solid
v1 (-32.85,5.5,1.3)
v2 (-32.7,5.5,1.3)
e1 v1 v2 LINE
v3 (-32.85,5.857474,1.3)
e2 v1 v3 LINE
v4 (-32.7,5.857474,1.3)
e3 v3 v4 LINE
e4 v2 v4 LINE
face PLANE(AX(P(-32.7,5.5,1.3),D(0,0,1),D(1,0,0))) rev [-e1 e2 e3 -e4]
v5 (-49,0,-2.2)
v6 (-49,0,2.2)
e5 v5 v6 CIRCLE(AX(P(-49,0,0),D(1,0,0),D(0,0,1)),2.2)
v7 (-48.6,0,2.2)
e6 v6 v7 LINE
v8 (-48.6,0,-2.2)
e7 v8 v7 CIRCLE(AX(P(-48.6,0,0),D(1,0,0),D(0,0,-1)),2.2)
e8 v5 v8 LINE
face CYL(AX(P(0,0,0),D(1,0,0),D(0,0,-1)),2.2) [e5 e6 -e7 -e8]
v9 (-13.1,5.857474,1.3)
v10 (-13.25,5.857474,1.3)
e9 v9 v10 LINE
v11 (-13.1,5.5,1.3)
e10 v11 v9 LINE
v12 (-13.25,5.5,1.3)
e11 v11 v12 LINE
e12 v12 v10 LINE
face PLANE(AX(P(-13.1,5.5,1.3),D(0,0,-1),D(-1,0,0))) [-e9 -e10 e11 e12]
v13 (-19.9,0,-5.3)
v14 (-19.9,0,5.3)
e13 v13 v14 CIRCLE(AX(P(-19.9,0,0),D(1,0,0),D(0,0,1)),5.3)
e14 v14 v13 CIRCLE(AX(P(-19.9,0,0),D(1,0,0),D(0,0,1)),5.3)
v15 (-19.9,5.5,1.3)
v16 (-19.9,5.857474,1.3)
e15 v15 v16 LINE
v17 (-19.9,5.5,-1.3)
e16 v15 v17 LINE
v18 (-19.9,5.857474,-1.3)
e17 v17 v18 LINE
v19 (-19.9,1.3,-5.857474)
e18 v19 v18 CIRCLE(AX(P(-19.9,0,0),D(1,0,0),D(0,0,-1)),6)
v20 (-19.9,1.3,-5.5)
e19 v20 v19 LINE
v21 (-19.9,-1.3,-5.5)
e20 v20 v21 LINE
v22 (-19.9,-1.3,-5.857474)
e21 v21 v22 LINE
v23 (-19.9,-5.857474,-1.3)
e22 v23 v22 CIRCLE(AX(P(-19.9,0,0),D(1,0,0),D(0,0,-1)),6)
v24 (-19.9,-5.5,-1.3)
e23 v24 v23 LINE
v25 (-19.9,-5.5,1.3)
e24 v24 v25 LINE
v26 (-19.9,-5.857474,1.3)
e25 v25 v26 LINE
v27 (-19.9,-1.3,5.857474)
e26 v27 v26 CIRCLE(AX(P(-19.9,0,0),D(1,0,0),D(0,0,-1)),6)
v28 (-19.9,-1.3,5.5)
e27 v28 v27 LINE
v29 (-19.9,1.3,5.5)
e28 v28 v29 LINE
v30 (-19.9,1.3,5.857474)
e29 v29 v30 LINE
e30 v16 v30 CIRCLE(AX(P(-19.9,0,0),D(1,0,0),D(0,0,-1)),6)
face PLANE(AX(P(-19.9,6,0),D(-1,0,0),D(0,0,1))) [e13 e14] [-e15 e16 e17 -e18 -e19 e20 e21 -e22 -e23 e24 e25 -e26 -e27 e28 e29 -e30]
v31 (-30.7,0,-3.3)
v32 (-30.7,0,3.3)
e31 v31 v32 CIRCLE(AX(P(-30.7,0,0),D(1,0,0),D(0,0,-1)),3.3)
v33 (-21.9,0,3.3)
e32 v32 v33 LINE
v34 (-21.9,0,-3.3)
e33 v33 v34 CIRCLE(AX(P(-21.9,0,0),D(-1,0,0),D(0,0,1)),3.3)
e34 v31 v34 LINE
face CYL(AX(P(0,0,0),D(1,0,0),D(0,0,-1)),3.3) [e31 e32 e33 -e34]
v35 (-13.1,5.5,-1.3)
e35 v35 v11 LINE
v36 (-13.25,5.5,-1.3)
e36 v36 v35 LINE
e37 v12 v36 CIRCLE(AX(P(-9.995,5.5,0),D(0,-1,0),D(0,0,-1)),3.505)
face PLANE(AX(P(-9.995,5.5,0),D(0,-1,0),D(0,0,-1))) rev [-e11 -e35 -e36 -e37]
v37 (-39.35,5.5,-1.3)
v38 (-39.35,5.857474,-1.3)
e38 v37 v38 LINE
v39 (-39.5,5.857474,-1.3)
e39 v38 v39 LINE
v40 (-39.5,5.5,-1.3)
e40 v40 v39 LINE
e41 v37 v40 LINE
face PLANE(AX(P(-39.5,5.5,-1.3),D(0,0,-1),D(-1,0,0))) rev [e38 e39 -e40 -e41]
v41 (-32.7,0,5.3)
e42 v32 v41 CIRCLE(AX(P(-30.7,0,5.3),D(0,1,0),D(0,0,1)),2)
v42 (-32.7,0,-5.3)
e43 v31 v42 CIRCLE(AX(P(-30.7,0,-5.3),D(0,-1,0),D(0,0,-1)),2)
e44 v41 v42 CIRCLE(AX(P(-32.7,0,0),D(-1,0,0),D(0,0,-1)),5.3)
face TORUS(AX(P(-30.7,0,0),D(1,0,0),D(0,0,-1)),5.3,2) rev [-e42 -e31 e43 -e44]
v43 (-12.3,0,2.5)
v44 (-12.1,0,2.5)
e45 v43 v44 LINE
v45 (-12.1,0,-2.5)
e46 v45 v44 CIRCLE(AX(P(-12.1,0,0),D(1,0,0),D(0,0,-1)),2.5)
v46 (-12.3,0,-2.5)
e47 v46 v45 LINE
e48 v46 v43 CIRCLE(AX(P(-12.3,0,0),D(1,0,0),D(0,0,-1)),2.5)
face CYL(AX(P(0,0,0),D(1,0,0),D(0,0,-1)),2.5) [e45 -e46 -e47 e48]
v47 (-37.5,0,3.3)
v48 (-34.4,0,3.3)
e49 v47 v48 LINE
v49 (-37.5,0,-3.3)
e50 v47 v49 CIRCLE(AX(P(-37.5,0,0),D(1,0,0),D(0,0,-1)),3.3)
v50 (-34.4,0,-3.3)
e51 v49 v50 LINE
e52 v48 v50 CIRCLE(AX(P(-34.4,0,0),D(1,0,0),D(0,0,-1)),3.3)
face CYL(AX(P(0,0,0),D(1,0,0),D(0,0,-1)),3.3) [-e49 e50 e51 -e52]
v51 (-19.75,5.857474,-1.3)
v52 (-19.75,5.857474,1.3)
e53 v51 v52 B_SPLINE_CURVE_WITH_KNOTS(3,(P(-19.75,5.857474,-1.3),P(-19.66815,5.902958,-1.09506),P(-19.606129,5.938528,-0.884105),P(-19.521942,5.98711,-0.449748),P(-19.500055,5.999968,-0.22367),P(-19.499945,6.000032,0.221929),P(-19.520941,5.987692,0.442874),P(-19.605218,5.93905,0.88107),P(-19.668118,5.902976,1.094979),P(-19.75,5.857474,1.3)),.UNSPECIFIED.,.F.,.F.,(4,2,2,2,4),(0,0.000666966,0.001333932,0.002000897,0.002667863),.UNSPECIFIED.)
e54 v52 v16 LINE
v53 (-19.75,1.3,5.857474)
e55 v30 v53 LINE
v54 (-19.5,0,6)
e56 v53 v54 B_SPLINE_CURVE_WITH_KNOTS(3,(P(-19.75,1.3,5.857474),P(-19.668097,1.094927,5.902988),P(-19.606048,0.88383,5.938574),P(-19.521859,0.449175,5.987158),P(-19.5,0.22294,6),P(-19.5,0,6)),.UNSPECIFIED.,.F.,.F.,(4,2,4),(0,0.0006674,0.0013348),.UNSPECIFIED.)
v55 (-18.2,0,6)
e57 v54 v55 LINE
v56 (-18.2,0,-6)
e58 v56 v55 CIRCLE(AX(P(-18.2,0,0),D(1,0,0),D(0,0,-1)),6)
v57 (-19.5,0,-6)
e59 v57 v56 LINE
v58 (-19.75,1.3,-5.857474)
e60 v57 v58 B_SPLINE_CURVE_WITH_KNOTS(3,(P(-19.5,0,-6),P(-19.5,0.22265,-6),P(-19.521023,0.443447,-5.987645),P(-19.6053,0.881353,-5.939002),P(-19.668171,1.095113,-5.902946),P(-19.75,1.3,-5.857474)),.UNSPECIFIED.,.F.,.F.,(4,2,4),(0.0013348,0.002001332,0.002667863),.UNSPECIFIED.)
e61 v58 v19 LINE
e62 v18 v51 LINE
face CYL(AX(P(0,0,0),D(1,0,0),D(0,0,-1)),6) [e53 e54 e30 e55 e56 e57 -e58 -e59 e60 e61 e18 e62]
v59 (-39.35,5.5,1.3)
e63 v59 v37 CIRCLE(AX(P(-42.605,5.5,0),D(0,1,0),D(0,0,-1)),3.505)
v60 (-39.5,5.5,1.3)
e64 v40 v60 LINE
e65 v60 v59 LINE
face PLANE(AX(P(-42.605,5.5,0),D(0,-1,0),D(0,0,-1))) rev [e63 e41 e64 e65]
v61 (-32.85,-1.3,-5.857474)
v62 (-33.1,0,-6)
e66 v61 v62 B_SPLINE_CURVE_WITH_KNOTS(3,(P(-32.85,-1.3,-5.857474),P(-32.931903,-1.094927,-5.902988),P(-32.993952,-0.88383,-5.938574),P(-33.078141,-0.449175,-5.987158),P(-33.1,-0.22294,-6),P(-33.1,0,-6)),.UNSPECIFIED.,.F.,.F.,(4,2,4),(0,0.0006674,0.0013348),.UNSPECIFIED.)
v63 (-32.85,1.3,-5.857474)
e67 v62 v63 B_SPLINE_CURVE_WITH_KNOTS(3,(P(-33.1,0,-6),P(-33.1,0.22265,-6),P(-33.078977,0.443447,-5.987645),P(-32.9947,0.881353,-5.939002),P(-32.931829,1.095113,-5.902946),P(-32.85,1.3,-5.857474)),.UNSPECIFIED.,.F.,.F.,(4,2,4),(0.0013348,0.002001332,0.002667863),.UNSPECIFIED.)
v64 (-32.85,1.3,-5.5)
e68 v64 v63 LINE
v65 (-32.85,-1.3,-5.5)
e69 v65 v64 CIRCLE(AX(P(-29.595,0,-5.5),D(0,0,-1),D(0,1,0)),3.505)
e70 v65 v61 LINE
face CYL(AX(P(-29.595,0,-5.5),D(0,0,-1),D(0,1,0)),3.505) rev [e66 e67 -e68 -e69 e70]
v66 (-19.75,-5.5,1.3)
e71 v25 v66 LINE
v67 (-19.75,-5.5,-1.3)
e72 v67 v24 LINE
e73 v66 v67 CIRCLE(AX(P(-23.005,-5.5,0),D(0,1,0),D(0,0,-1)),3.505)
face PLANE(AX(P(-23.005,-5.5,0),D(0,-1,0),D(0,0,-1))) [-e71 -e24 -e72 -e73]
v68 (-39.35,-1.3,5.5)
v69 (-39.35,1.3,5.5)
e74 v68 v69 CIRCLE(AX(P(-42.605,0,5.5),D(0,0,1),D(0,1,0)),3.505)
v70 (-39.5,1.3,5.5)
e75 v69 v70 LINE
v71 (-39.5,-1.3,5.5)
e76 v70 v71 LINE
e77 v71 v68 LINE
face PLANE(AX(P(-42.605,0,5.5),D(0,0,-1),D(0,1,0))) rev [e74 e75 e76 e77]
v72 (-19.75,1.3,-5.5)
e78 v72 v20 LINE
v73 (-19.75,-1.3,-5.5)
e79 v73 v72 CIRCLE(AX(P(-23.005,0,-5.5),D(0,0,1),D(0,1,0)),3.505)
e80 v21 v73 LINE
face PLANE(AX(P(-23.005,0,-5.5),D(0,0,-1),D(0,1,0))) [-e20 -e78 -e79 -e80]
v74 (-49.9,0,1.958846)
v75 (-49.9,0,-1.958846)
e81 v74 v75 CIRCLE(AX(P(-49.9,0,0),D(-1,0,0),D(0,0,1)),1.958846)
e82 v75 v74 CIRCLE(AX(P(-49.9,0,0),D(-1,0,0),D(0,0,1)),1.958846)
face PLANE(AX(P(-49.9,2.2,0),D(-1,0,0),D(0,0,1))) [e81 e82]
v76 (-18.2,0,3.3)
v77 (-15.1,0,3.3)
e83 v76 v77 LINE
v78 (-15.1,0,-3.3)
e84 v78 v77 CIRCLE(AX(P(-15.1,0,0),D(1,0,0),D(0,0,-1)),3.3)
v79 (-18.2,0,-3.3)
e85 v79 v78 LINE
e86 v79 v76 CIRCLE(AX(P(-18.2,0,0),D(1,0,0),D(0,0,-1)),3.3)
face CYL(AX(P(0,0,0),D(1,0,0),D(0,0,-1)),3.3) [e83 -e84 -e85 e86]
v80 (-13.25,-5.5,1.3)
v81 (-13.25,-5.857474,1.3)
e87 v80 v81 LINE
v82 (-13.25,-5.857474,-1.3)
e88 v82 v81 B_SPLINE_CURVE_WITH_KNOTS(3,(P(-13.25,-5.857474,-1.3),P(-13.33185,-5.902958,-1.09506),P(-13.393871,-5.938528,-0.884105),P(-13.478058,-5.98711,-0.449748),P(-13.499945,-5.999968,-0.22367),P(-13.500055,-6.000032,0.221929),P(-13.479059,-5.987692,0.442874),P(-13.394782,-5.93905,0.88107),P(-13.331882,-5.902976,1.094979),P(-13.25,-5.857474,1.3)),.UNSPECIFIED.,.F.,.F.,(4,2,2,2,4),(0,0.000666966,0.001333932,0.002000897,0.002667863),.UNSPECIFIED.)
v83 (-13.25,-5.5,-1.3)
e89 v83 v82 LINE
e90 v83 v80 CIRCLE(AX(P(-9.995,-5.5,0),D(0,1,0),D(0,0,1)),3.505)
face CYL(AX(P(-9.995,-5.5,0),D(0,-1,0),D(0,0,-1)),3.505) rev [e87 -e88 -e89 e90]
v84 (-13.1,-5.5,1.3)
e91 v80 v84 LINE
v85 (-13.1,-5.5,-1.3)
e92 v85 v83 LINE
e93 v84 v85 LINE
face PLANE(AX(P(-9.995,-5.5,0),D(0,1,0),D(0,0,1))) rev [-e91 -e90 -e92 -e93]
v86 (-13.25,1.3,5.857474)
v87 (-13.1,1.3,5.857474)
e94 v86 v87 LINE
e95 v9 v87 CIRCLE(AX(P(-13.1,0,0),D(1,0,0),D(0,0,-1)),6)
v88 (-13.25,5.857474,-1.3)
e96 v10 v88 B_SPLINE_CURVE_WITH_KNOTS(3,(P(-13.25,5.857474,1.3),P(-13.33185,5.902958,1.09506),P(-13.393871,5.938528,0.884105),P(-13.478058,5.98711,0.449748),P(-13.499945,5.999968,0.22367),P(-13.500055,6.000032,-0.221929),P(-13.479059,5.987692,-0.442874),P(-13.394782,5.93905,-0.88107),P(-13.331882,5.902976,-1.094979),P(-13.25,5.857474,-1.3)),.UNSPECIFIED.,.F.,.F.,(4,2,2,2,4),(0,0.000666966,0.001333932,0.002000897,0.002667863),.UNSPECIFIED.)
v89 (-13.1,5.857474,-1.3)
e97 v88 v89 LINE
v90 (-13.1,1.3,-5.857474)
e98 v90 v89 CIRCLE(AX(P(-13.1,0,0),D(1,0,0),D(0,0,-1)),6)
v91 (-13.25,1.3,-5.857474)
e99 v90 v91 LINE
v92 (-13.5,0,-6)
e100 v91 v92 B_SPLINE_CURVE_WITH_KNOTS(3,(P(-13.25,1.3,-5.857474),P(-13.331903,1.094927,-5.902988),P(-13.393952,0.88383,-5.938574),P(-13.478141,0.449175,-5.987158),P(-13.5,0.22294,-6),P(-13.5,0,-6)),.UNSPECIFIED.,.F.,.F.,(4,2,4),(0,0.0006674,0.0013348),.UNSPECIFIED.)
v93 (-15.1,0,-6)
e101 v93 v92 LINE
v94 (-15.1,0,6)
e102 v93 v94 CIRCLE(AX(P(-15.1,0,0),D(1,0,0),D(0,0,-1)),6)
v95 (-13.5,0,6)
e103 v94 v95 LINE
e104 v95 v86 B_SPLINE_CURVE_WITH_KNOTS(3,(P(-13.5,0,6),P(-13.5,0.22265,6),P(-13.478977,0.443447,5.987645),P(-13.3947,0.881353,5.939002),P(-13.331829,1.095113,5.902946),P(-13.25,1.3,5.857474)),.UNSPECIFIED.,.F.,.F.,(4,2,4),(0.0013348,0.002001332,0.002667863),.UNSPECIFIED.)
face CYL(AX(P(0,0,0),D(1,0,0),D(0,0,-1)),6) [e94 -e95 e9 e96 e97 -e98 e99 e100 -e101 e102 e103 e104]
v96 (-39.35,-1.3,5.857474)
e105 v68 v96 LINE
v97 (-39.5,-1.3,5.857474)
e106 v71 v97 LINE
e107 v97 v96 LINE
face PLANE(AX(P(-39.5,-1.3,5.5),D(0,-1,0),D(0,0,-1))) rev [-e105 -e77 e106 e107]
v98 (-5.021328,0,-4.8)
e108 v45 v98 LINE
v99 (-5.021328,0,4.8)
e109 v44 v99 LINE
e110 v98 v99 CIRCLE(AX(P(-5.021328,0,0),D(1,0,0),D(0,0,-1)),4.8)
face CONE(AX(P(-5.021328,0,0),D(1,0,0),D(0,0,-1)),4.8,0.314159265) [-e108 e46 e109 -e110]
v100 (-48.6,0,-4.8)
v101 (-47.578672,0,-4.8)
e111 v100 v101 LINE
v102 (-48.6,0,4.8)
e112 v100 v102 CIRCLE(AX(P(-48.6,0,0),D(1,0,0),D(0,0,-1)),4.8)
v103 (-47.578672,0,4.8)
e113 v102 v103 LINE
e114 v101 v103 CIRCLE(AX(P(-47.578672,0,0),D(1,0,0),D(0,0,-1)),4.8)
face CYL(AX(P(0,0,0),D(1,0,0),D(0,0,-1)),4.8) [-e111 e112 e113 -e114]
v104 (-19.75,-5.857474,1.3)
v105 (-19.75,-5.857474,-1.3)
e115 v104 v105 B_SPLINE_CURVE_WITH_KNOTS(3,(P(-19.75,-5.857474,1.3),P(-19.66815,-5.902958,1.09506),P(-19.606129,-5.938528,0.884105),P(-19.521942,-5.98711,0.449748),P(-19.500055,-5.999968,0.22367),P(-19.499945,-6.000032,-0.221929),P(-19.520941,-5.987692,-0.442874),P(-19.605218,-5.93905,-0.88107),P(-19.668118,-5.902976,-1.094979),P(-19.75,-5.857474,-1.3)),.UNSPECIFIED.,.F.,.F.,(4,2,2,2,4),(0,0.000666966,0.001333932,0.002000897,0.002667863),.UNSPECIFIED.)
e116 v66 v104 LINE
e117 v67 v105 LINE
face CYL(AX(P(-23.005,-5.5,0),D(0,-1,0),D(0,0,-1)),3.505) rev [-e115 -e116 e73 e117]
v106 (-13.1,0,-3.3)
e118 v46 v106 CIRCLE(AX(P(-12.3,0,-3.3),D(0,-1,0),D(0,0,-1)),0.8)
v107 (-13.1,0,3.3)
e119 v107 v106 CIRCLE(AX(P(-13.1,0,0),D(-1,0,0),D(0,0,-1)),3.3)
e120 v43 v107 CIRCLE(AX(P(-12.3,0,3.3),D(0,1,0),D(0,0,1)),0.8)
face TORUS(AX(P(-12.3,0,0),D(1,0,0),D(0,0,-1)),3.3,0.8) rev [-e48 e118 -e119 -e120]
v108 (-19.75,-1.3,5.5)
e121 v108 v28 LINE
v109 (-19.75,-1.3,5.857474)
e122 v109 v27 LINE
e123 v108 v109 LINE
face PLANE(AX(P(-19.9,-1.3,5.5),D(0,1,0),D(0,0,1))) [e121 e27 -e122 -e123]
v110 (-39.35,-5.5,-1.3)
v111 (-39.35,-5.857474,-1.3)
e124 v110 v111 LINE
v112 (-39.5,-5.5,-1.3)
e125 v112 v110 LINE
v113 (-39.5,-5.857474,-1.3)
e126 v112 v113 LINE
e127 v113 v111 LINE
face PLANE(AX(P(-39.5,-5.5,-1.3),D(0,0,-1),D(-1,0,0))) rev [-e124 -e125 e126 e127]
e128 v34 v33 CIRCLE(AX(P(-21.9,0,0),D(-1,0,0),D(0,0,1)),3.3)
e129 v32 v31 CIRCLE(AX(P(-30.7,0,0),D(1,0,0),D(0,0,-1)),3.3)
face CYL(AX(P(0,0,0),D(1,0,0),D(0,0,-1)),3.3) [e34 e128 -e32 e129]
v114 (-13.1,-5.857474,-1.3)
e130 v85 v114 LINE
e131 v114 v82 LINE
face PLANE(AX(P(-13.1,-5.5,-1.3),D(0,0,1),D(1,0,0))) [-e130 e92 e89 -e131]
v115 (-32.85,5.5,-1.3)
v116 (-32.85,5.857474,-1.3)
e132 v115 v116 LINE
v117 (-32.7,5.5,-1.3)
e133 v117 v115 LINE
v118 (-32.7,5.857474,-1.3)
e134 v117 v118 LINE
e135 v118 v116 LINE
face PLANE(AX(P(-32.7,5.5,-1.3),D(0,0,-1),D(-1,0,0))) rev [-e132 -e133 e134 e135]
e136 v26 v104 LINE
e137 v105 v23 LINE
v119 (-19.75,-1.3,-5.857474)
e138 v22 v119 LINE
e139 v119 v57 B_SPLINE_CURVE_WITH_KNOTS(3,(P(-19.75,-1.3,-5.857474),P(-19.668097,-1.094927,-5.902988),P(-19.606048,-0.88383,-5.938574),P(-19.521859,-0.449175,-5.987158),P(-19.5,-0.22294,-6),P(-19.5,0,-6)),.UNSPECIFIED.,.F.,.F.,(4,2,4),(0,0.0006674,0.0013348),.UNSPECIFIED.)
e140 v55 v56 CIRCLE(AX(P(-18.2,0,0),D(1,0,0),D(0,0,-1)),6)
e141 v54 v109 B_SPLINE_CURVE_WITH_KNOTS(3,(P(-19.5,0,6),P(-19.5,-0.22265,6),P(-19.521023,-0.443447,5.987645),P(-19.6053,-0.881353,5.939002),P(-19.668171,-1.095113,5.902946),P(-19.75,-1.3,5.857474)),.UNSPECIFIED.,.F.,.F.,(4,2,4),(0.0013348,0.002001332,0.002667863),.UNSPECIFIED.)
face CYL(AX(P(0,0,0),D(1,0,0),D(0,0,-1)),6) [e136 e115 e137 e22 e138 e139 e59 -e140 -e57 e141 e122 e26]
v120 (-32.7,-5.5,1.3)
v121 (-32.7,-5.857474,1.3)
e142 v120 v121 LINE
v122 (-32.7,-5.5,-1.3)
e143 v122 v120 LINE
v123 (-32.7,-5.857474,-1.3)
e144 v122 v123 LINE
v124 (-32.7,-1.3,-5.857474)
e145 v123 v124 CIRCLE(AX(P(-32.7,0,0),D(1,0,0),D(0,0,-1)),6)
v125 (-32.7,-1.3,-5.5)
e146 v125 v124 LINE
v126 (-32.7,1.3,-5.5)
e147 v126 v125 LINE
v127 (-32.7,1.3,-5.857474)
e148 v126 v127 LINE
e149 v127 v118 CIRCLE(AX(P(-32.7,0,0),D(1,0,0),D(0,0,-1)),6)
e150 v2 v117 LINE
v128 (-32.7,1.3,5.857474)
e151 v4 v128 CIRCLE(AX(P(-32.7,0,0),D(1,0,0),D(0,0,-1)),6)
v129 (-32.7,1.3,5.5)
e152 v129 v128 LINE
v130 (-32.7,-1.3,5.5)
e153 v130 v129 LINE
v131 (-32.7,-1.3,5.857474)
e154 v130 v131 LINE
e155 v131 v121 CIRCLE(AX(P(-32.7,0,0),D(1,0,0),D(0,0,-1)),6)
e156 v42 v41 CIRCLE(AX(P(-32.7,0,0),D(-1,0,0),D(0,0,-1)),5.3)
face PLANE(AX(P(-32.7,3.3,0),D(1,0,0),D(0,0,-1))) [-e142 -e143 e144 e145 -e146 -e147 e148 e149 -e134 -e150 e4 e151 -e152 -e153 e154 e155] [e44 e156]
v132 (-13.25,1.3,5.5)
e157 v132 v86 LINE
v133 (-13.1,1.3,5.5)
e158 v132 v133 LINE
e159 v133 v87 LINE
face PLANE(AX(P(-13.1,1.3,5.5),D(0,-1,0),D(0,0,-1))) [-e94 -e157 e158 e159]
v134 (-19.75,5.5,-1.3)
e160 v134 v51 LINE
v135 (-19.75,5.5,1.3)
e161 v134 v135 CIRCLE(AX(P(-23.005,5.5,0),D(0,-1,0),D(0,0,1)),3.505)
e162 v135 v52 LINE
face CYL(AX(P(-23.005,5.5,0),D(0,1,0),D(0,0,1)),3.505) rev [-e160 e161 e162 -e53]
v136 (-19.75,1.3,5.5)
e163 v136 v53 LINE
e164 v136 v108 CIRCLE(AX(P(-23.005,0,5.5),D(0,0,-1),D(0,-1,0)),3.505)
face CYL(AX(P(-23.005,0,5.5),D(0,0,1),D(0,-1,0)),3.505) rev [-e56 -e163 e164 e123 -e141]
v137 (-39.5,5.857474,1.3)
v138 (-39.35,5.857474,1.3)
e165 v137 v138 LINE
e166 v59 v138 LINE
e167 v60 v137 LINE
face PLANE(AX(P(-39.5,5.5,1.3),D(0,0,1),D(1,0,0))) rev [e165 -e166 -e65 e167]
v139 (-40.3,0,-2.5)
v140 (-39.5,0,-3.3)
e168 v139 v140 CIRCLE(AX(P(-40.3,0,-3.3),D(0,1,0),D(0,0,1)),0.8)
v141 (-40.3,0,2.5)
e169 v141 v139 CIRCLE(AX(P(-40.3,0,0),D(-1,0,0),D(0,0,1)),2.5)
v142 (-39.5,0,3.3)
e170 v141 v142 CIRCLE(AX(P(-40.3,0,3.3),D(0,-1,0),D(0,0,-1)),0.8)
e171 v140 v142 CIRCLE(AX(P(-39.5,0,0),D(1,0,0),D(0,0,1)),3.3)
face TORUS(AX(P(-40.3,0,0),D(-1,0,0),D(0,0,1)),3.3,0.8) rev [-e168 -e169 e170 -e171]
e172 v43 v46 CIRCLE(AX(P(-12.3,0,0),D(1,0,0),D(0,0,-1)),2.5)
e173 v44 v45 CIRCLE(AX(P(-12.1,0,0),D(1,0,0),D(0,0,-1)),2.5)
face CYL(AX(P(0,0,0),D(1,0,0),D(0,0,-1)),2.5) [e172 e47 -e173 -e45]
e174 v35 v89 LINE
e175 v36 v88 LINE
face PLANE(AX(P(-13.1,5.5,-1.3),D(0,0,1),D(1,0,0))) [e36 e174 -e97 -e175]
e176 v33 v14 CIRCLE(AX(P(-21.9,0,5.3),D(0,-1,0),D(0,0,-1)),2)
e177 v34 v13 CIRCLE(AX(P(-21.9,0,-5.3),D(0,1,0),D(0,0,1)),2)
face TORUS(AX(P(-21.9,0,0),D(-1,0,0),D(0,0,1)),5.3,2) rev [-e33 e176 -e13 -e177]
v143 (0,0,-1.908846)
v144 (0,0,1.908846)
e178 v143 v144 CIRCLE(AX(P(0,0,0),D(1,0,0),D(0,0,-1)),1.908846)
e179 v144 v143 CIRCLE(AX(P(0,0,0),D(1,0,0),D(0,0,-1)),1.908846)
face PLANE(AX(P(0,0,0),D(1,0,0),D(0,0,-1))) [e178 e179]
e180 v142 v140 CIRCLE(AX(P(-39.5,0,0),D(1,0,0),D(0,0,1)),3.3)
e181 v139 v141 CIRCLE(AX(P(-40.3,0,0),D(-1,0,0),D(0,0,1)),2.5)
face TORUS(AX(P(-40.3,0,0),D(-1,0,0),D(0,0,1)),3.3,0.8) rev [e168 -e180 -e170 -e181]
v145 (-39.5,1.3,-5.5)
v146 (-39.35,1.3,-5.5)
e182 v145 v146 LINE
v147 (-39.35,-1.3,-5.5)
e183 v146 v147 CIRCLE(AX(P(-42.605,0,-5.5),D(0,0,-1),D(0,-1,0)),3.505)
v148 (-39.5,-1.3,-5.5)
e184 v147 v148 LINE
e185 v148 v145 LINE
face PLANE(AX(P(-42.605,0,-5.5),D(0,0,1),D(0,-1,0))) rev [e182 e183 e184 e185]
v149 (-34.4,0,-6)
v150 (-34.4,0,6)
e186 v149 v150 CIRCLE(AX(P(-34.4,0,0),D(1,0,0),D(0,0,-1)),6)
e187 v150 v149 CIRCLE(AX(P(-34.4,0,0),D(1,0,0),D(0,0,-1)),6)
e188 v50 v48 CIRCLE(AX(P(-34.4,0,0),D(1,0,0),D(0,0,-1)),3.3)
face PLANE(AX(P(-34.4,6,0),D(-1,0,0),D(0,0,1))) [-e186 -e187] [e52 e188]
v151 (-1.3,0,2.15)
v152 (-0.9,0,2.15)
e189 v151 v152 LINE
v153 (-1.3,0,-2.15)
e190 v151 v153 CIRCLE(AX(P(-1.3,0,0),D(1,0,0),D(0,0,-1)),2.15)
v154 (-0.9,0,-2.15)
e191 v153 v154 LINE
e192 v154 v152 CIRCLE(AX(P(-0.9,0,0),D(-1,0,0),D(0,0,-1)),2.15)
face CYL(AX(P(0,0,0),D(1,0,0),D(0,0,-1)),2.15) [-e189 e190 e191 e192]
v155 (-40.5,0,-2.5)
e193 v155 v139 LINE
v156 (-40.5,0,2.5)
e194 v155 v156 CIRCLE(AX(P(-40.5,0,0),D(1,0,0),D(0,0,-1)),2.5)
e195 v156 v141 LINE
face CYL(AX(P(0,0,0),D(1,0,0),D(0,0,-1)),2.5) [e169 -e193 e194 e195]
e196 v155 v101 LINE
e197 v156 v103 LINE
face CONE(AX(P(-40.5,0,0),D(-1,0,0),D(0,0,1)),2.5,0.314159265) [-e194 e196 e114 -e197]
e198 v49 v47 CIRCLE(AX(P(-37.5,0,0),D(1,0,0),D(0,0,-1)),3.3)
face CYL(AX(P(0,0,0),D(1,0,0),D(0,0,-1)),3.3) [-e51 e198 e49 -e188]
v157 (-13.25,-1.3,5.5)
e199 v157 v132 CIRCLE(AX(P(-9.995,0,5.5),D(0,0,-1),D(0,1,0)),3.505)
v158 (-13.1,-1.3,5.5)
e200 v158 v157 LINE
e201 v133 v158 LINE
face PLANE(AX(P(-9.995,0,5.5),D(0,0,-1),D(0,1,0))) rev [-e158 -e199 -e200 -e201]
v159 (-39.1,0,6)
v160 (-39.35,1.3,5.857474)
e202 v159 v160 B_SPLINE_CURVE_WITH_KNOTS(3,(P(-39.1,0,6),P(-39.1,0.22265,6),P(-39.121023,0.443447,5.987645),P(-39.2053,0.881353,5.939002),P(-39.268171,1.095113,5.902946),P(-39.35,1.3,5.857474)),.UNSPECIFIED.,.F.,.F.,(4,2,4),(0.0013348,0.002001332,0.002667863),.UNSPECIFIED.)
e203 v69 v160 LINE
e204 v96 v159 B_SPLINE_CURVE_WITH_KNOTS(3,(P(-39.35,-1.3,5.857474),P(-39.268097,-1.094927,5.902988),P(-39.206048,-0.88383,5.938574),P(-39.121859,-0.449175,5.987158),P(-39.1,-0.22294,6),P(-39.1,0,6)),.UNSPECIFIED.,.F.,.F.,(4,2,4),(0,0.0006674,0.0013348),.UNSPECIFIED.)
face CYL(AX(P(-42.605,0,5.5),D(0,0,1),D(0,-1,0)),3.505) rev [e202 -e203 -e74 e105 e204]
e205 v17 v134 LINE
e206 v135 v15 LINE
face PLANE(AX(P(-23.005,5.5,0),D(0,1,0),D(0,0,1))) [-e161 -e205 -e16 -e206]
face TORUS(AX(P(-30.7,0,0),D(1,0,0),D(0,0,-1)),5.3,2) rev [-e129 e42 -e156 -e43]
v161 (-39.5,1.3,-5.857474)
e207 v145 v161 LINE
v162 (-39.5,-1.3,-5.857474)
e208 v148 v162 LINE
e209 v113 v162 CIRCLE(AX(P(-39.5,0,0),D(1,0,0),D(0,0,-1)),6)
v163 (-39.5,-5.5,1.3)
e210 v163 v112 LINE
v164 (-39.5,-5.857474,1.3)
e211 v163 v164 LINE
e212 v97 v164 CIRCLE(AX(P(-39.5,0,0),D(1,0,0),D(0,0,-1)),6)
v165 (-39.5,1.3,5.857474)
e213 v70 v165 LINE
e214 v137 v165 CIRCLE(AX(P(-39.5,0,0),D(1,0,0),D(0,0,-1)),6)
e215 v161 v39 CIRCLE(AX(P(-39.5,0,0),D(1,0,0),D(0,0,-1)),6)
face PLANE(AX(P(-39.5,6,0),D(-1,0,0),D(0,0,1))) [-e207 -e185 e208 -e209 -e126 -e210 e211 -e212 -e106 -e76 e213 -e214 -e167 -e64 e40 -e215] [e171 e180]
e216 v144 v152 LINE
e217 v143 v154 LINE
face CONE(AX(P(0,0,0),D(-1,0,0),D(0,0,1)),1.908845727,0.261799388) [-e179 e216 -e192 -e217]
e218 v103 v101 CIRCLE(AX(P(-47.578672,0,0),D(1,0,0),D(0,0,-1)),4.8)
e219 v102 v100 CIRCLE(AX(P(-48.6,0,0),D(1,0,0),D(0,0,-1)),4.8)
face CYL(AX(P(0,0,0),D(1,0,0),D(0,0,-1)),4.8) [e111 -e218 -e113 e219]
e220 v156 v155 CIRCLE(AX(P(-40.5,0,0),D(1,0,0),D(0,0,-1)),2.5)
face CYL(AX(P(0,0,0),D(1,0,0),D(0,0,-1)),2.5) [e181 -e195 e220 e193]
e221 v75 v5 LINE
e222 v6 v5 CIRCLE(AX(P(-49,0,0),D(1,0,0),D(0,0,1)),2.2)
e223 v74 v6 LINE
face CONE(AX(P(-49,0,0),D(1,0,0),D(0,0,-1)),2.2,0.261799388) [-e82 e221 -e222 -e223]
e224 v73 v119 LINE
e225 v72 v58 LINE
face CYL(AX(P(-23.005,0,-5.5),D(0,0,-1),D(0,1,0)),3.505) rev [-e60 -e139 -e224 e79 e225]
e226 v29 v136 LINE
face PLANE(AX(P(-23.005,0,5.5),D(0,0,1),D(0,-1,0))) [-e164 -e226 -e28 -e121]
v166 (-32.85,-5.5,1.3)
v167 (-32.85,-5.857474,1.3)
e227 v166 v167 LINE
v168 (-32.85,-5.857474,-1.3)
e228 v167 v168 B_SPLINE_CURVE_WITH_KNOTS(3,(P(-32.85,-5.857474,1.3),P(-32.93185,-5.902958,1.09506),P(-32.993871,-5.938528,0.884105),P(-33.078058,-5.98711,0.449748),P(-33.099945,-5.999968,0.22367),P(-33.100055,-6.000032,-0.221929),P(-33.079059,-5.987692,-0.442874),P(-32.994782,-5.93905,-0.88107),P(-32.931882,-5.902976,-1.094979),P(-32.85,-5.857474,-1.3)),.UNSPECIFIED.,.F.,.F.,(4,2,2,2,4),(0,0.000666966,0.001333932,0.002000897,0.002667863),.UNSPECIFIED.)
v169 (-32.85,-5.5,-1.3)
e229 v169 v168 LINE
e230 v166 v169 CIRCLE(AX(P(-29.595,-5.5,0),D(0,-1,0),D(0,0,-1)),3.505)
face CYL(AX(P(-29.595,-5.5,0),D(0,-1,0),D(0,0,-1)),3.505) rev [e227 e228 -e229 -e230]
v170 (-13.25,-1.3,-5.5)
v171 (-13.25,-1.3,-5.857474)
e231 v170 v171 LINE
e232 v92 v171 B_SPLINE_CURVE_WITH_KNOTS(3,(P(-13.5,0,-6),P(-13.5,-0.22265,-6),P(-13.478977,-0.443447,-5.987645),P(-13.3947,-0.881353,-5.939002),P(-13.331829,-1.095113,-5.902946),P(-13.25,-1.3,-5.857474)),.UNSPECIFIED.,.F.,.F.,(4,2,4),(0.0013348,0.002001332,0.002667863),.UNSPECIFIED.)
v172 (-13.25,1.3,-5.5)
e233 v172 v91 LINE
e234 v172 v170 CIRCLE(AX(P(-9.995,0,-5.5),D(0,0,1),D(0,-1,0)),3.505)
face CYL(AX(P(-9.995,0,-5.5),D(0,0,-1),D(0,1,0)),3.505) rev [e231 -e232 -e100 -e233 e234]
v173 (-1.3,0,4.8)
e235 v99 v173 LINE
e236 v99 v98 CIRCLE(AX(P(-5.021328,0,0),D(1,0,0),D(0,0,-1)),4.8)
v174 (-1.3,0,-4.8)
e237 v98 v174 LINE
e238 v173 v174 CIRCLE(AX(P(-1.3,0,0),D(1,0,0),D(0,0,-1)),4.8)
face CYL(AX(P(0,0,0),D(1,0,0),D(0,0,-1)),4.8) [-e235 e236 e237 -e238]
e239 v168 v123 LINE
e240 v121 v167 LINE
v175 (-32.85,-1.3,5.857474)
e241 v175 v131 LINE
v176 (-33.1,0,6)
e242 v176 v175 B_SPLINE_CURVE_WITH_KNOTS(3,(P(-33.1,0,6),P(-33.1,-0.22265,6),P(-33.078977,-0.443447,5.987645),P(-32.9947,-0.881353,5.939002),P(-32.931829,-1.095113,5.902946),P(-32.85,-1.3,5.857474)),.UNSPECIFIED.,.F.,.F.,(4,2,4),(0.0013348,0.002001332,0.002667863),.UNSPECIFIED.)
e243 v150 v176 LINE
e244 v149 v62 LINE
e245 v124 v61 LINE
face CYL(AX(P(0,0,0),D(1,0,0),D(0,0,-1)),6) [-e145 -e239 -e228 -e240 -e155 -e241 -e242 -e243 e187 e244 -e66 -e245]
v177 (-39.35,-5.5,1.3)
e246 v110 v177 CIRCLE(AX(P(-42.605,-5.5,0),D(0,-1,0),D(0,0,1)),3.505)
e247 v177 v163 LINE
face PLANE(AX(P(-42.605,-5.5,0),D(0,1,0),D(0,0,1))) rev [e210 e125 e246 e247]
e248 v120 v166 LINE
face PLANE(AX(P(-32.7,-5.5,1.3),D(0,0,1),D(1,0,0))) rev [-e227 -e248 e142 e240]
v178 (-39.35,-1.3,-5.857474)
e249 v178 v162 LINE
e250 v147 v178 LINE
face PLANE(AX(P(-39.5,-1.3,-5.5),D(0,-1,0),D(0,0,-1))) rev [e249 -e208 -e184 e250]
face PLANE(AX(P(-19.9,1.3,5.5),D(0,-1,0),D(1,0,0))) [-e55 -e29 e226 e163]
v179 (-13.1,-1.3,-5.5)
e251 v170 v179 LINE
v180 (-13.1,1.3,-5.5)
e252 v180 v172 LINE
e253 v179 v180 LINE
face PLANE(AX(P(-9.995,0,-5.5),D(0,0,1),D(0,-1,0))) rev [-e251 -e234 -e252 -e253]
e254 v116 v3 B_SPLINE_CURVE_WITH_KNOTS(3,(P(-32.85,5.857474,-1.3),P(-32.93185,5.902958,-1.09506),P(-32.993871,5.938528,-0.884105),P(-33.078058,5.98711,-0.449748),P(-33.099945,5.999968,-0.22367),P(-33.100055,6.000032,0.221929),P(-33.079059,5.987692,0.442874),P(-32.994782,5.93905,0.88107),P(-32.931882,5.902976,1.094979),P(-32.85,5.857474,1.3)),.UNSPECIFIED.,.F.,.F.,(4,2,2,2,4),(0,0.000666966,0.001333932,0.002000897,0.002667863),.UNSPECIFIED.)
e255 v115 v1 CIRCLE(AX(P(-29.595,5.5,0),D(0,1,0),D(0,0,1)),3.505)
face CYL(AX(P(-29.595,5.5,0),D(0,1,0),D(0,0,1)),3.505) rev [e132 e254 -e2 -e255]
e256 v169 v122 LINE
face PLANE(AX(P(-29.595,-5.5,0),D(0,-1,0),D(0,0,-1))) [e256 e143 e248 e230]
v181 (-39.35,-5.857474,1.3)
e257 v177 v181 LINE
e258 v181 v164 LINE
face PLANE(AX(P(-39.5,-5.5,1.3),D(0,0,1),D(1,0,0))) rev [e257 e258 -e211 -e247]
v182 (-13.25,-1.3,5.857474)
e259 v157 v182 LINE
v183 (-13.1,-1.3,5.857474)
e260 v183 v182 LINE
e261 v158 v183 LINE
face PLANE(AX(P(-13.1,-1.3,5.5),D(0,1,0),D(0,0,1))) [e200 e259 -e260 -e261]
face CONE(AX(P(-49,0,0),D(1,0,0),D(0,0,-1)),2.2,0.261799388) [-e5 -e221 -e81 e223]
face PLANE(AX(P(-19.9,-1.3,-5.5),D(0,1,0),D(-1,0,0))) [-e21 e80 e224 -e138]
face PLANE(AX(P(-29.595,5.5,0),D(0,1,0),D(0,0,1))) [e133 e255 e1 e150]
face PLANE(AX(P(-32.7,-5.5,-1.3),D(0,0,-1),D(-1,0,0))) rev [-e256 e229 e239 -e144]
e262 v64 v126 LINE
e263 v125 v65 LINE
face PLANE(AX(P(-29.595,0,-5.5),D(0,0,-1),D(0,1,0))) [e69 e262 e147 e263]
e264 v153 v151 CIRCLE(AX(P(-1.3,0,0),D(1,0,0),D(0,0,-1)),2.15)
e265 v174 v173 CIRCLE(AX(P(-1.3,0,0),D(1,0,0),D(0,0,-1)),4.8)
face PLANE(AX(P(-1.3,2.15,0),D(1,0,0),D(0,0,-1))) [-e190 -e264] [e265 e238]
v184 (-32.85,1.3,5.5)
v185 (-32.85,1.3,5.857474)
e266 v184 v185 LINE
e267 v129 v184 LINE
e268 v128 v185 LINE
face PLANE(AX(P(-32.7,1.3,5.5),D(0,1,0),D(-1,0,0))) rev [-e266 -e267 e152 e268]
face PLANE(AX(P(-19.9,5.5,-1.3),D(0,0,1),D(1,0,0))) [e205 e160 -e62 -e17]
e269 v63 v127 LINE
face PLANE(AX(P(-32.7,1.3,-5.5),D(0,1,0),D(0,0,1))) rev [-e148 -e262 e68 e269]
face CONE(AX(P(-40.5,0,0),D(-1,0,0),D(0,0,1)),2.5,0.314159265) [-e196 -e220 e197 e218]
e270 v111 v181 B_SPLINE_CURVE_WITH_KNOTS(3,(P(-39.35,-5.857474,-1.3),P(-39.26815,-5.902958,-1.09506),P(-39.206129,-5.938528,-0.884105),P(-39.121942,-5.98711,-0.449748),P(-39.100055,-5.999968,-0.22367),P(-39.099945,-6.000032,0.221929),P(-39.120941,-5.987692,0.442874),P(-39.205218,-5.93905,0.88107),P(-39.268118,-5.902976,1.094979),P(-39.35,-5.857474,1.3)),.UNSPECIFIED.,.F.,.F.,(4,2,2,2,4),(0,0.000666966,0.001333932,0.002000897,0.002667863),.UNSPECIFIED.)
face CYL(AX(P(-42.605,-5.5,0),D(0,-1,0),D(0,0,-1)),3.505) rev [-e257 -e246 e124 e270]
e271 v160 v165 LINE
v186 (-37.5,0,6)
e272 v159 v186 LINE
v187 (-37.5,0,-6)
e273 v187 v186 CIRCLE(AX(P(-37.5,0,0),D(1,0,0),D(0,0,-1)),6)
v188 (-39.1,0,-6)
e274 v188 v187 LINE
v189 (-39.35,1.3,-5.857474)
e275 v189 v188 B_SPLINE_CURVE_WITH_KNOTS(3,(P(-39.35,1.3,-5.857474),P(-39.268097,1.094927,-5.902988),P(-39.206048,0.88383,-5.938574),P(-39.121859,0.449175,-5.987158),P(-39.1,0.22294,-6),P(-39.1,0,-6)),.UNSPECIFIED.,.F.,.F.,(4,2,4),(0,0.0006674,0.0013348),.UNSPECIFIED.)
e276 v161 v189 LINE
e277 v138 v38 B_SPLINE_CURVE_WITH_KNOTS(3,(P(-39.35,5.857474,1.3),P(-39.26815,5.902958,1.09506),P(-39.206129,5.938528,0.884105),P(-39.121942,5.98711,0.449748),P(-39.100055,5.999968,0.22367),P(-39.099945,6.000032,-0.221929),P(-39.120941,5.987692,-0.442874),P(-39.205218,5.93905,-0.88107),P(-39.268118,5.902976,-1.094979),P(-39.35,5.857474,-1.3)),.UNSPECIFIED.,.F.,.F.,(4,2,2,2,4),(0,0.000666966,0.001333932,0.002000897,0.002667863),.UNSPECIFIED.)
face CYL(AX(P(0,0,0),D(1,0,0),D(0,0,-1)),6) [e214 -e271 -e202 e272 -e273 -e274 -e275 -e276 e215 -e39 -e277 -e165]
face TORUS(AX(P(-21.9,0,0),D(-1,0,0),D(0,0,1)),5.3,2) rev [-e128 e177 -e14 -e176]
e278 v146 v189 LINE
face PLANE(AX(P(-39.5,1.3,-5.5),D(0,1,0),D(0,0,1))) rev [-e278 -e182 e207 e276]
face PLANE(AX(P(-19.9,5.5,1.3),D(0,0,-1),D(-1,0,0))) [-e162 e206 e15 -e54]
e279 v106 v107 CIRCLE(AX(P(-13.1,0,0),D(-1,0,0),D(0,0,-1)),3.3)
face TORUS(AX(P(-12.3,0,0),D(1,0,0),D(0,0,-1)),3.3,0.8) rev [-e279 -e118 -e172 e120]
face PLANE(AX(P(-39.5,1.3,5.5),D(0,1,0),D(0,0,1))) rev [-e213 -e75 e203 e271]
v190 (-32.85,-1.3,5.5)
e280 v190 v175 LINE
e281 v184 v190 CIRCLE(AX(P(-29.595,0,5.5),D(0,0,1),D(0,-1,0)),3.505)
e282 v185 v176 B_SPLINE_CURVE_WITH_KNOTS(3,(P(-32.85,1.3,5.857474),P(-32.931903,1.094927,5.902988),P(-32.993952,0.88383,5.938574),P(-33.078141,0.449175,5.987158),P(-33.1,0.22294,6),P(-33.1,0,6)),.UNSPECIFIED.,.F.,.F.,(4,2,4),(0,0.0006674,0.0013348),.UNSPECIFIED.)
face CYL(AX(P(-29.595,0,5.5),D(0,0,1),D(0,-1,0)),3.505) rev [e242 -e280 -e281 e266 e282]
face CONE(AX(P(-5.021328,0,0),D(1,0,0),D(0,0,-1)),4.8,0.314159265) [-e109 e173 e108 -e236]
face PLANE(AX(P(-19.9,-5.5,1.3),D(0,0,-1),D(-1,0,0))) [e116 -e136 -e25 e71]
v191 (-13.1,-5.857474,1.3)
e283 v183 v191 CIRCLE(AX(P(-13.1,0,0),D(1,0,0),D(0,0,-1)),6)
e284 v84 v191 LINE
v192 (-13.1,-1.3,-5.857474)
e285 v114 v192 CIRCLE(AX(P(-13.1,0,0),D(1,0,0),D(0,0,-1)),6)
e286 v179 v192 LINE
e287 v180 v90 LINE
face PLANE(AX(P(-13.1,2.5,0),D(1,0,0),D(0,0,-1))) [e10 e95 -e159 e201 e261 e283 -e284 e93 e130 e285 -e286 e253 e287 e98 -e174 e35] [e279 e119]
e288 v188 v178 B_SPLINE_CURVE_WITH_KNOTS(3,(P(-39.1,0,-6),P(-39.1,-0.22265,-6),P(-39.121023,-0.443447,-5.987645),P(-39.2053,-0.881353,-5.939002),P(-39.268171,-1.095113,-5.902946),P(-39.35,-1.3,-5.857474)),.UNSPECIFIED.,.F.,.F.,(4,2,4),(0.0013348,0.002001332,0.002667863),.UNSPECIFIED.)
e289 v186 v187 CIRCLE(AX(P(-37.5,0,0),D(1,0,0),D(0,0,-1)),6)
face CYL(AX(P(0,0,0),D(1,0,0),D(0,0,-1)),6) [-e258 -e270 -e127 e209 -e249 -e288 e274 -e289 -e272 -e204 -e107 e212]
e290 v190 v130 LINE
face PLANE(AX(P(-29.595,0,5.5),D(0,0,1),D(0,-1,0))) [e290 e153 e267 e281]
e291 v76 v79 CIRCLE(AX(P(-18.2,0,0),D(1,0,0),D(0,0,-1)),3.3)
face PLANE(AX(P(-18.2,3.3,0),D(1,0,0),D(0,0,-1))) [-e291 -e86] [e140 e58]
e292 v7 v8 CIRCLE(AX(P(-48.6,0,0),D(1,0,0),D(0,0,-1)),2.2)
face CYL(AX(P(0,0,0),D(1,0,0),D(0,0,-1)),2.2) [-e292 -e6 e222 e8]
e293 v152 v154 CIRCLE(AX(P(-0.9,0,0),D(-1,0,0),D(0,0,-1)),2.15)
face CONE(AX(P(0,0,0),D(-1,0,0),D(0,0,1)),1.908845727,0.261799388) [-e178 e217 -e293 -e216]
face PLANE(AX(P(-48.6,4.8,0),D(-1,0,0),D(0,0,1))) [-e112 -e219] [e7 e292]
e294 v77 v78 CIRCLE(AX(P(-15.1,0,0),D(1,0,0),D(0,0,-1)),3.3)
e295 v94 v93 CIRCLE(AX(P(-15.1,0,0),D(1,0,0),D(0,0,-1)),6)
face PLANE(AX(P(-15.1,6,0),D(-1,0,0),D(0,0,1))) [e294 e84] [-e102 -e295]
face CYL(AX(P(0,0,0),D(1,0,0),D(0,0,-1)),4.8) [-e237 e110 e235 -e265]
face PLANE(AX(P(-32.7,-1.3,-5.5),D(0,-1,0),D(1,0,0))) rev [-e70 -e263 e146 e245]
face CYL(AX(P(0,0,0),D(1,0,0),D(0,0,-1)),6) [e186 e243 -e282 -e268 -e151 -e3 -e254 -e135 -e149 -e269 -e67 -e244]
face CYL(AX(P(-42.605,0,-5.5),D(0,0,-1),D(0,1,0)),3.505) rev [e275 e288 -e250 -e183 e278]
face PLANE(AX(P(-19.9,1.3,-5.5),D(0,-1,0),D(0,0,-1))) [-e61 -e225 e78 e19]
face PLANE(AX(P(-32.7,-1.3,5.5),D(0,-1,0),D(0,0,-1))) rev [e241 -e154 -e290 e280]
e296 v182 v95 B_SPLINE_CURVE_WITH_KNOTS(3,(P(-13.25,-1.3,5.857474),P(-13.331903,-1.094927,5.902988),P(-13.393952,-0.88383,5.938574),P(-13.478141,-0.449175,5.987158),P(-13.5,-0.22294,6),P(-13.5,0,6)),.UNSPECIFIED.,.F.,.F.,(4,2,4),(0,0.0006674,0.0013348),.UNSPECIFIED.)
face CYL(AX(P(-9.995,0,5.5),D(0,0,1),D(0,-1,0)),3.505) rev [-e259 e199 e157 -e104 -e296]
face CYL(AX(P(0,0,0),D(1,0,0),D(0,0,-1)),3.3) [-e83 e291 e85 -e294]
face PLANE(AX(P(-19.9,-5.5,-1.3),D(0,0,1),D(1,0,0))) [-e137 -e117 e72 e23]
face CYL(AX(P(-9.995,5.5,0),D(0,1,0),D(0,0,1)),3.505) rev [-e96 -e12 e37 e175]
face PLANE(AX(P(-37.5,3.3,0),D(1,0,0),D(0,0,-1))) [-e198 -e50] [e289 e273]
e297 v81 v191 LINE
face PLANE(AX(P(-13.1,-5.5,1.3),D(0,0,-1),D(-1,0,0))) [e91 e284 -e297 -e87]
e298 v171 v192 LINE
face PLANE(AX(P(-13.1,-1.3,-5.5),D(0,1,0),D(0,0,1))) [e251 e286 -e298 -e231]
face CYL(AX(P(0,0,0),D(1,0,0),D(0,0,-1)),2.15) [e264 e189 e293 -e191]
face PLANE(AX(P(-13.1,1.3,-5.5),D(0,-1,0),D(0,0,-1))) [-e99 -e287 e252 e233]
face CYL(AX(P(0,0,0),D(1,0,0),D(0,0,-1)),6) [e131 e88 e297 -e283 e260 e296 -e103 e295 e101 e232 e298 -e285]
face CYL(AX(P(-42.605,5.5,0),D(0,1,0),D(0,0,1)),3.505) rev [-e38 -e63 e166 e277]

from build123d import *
from OCP.BRepFilletAPI import BRepFilletAPI_MakeChamfer

# Parameters (mm, degrees)
FILLET1_R            = 0.8
FILLET3_R            = 2
CHAMFER1_SIZE        = 0.9
CHAMFER1_SIZE2       = 0.241154273
CUT_EXTRUDE1_START   = 15.5
CUT_EXTRUDE1_DEPTH   = 10
CIRPATTERN1_COUNT    = 4
MIRROR1_START        = 15.5
MIRROR1_COPY_1_DEPTH = 10
MIRROR1_COPY_2_DEPTH = 10
MIRROR1_COPY_3_DEPTH = 10


with BuildPart() as part:
    # Sketch1 → Revolve1 (revolve)
    with BuildSketch(Plane.XY, mode=Mode.PRIVATE) as revolve1_sk:
        Polygon((0, 0), (0, 2.15), (-1.3, 2.15), (-1.3, 4.8), (-5.021327864, 4.8), (-12.1, 2.5), (-13.1, 2.5), (-13.1, 6), (-15.1, 6), (-15.1, 3.3), (-18.2, 3.3), (-18.2, 6), (-19.9, 6), (-19.9, 3.3), (-32.7, 3.3), (-32.7, 6), (-34.4, 6), (-34.4, 3.3), (-37.5, 3.3), (-37.5, 6), (-39.5, 6), (-39.5, 2.5), (-40.5, 2.5), (-47.578672136, 4.8), (-48.6, 4.8), (-48.6, 2.2), (-49.9, 2.2), (-49.9, 0), align=None)
    revolve(revolve1_sk.sketch.rotate(Axis((0, 0, 0), (-1, 0, 0)), 90), axis=Axis((0, 0, 0), (-1, 0, 0)))

    # Fillet1
    fillet1_edges = [part.edges().sort_by_distance(p)[0] for p in [
        (-39.5, 0, 2.5),
        (-13.1, 0, 2.5),
    ]]
    fillet(fillet1_edges, radius=FILLET1_R)

    # Fillet3
    fillet3_edges = [part.edges().sort_by_distance(p)[0] for p in [
        (-32.7, 0, 3.3),
        (-19.9, 0, 3.3),
    ]]
    fillet(fillet3_edges, radius=FILLET3_R)

    # Chamfer1: one chamfer whose edges measure the first distance from different faces: ONE call of the kernel's chamfer builder (chamfer() names one face for all edges)
    chamfer1_edges_1 = [part.edges().sort_by_distance(p)[0] for p in [
        (-49.9, 0, 2.2),
    ]]
    chamfer1_side_1 = [part.faces().sort_by_distance(p)[0] for p in [
        (-49.25, 0, 2.2),
    ]]
    chamfer1_edges_2 = [part.edges().sort_by_distance(p)[0] for p in [
        (0, 0, 2.15),
    ]]
    chamfer1_side_2 = [part.faces().sort_by_distance(p)[0] for p in [
        (-0.65, 0, 2.15),
    ]]
    chamfer1 = BRepFilletAPI_MakeChamfer(part.part.solid().wrapped)
    for e in chamfer1_edges_1:
        chamfer1.Add(CHAMFER1_SIZE, CHAMFER1_SIZE2, e.wrapped, chamfer1_side_1[0].wrapped)  # the first distance lies on this face
    for e in chamfer1_edges_2:
        chamfer1.Add(CHAMFER1_SIZE, CHAMFER1_SIZE2, e.wrapped, chamfer1_side_2[0].wrapped)  # the first distance lies on this face
    add(Compound.cast(chamfer1.Shape()), mode=Mode.REPLACE)

    # Sketch2 → Cut-Extrude1 (cut)
    with BuildSketch(Plane(origin=(0, 0, 0), x_dir=(1, 0, 0), z_dir=(0, 1, 0)).offset(CUT_EXTRUDE1_START)):
        with BuildLine():
            Line((-39.5, 1.3), (-39.35, 1.3))
            ThreePointArc((-39.35, 1.3), (-39.1, 0), (-39.35, -1.3))
            Line((-39.35, -1.3), (-39.5, -1.3))
            Line((-39.5, -1.3), (-39.5, 1.3))
        make_face()
        with BuildLine():
            Line((-32.7, 1.3), (-32.85, 1.3))
            ThreePointArc((-32.85, 1.3), (-33.1, 0), (-32.85, -1.3))
            Line((-32.85, -1.3), (-32.7, -1.3))
            Line((-32.7, -1.3), (-32.7, 1.3))
        make_face()
    cut_extrude1 = extrude(amount=-CUT_EXTRUDE1_DEPTH, mode=Mode.SUBTRACT)

    # CirPattern1: Cut-Extrude1 ×4 about axis
    cirpattern1_axis = Axis((0, 0, 0), (1, 0, 0))
    for i in range(1, CIRPATTERN1_COUNT):
        add(cut_extrude1.rotate(cirpattern1_axis, i * 360 / CIRPATTERN1_COUNT), mode=Mode.SUBTRACT)

    # Mirror1: Cut-Extrude1 across plane
    add(cut_extrude1.mirror(Plane(origin=(-26.3, 0, 0), x_dir=(0, 0, 1), z_dir=(1, 0, 0))), mode=Mode.SUBTRACT)

    # Mirror1 copy 1 sketch → Mirror1 copy 1 (cut)
    with BuildSketch(Plane(origin=(-52.6, 0, 0), x_dir=(-1, 0, 0), z_dir=(0, 0, 1)).offset(MIRROR1_START)):
        with BuildLine():
            Line((-39.5, -1.3), (-39.35, -1.3))
            ThreePointArc((-39.35, -1.3), (-39.1, 0), (-39.35, 1.3))
            Line((-39.35, 1.3), (-39.5, 1.3))
            Line((-39.5, 1.3), (-39.5, -1.3))
        make_face()
        with BuildLine():
            Line((-32.7, -1.3), (-32.85, -1.3))
            ThreePointArc((-32.85, -1.3), (-33.1, 0), (-32.85, 1.3))
            Line((-32.85, 1.3), (-32.7, 1.3))
            Line((-32.7, 1.3), (-32.7, -1.3))
        make_face()
    extrude(amount=-MIRROR1_COPY_1_DEPTH, mode=Mode.SUBTRACT)

    # Mirror1 copy 2 sketch → Mirror1 copy 2 (cut)
    with BuildSketch(Plane(origin=(-52.6, 0, 0), x_dir=(-1, 0, 0), z_dir=(0, -1, 0)).offset(MIRROR1_START)):
        with BuildLine():
            Line((-39.5, -1.3), (-39.35, -1.3))
            ThreePointArc((-39.35, -1.3), (-39.1, 0), (-39.35, 1.3))
            Line((-39.35, 1.3), (-39.5, 1.3))
            Line((-39.5, 1.3), (-39.5, -1.3))
        make_face()
        with BuildLine():
            Line((-32.7, -1.3), (-32.85, -1.3))
            ThreePointArc((-32.85, -1.3), (-33.1, 0), (-32.85, 1.3))
            Line((-32.85, 1.3), (-32.7, 1.3))
            Line((-32.7, 1.3), (-32.7, -1.3))
        make_face()
    extrude(amount=-MIRROR1_COPY_2_DEPTH, mode=Mode.SUBTRACT)

    # Mirror1 copy 3 sketch → Mirror1 copy 3 (cut)
    with BuildSketch(Plane(origin=(-52.6, 0, 0), x_dir=(-1, 0, 0), z_dir=(0, 0, -1)).offset(MIRROR1_START)):
        with BuildLine():
            Line((-39.5, -1.3), (-39.35, -1.3))
            ThreePointArc((-39.35, -1.3), (-39.1, 0), (-39.35, 1.3))
            Line((-39.35, 1.3), (-39.5, 1.3))
            Line((-39.5, 1.3), (-39.5, -1.3))
        make_face()
        with BuildLine():
            Line((-32.7, -1.3), (-32.85, -1.3))
            ThreePointArc((-32.85, -1.3), (-33.1, 0), (-32.85, 1.3))
            Line((-32.85, 1.3), (-32.7, 1.3))
            Line((-32.7, 1.3), (-32.7, -1.3))
        make_face()
    extrude(amount=-MIRROR1_COPY_3_DEPTH, mode=Mode.SUBTRACT)


solid = part.part
